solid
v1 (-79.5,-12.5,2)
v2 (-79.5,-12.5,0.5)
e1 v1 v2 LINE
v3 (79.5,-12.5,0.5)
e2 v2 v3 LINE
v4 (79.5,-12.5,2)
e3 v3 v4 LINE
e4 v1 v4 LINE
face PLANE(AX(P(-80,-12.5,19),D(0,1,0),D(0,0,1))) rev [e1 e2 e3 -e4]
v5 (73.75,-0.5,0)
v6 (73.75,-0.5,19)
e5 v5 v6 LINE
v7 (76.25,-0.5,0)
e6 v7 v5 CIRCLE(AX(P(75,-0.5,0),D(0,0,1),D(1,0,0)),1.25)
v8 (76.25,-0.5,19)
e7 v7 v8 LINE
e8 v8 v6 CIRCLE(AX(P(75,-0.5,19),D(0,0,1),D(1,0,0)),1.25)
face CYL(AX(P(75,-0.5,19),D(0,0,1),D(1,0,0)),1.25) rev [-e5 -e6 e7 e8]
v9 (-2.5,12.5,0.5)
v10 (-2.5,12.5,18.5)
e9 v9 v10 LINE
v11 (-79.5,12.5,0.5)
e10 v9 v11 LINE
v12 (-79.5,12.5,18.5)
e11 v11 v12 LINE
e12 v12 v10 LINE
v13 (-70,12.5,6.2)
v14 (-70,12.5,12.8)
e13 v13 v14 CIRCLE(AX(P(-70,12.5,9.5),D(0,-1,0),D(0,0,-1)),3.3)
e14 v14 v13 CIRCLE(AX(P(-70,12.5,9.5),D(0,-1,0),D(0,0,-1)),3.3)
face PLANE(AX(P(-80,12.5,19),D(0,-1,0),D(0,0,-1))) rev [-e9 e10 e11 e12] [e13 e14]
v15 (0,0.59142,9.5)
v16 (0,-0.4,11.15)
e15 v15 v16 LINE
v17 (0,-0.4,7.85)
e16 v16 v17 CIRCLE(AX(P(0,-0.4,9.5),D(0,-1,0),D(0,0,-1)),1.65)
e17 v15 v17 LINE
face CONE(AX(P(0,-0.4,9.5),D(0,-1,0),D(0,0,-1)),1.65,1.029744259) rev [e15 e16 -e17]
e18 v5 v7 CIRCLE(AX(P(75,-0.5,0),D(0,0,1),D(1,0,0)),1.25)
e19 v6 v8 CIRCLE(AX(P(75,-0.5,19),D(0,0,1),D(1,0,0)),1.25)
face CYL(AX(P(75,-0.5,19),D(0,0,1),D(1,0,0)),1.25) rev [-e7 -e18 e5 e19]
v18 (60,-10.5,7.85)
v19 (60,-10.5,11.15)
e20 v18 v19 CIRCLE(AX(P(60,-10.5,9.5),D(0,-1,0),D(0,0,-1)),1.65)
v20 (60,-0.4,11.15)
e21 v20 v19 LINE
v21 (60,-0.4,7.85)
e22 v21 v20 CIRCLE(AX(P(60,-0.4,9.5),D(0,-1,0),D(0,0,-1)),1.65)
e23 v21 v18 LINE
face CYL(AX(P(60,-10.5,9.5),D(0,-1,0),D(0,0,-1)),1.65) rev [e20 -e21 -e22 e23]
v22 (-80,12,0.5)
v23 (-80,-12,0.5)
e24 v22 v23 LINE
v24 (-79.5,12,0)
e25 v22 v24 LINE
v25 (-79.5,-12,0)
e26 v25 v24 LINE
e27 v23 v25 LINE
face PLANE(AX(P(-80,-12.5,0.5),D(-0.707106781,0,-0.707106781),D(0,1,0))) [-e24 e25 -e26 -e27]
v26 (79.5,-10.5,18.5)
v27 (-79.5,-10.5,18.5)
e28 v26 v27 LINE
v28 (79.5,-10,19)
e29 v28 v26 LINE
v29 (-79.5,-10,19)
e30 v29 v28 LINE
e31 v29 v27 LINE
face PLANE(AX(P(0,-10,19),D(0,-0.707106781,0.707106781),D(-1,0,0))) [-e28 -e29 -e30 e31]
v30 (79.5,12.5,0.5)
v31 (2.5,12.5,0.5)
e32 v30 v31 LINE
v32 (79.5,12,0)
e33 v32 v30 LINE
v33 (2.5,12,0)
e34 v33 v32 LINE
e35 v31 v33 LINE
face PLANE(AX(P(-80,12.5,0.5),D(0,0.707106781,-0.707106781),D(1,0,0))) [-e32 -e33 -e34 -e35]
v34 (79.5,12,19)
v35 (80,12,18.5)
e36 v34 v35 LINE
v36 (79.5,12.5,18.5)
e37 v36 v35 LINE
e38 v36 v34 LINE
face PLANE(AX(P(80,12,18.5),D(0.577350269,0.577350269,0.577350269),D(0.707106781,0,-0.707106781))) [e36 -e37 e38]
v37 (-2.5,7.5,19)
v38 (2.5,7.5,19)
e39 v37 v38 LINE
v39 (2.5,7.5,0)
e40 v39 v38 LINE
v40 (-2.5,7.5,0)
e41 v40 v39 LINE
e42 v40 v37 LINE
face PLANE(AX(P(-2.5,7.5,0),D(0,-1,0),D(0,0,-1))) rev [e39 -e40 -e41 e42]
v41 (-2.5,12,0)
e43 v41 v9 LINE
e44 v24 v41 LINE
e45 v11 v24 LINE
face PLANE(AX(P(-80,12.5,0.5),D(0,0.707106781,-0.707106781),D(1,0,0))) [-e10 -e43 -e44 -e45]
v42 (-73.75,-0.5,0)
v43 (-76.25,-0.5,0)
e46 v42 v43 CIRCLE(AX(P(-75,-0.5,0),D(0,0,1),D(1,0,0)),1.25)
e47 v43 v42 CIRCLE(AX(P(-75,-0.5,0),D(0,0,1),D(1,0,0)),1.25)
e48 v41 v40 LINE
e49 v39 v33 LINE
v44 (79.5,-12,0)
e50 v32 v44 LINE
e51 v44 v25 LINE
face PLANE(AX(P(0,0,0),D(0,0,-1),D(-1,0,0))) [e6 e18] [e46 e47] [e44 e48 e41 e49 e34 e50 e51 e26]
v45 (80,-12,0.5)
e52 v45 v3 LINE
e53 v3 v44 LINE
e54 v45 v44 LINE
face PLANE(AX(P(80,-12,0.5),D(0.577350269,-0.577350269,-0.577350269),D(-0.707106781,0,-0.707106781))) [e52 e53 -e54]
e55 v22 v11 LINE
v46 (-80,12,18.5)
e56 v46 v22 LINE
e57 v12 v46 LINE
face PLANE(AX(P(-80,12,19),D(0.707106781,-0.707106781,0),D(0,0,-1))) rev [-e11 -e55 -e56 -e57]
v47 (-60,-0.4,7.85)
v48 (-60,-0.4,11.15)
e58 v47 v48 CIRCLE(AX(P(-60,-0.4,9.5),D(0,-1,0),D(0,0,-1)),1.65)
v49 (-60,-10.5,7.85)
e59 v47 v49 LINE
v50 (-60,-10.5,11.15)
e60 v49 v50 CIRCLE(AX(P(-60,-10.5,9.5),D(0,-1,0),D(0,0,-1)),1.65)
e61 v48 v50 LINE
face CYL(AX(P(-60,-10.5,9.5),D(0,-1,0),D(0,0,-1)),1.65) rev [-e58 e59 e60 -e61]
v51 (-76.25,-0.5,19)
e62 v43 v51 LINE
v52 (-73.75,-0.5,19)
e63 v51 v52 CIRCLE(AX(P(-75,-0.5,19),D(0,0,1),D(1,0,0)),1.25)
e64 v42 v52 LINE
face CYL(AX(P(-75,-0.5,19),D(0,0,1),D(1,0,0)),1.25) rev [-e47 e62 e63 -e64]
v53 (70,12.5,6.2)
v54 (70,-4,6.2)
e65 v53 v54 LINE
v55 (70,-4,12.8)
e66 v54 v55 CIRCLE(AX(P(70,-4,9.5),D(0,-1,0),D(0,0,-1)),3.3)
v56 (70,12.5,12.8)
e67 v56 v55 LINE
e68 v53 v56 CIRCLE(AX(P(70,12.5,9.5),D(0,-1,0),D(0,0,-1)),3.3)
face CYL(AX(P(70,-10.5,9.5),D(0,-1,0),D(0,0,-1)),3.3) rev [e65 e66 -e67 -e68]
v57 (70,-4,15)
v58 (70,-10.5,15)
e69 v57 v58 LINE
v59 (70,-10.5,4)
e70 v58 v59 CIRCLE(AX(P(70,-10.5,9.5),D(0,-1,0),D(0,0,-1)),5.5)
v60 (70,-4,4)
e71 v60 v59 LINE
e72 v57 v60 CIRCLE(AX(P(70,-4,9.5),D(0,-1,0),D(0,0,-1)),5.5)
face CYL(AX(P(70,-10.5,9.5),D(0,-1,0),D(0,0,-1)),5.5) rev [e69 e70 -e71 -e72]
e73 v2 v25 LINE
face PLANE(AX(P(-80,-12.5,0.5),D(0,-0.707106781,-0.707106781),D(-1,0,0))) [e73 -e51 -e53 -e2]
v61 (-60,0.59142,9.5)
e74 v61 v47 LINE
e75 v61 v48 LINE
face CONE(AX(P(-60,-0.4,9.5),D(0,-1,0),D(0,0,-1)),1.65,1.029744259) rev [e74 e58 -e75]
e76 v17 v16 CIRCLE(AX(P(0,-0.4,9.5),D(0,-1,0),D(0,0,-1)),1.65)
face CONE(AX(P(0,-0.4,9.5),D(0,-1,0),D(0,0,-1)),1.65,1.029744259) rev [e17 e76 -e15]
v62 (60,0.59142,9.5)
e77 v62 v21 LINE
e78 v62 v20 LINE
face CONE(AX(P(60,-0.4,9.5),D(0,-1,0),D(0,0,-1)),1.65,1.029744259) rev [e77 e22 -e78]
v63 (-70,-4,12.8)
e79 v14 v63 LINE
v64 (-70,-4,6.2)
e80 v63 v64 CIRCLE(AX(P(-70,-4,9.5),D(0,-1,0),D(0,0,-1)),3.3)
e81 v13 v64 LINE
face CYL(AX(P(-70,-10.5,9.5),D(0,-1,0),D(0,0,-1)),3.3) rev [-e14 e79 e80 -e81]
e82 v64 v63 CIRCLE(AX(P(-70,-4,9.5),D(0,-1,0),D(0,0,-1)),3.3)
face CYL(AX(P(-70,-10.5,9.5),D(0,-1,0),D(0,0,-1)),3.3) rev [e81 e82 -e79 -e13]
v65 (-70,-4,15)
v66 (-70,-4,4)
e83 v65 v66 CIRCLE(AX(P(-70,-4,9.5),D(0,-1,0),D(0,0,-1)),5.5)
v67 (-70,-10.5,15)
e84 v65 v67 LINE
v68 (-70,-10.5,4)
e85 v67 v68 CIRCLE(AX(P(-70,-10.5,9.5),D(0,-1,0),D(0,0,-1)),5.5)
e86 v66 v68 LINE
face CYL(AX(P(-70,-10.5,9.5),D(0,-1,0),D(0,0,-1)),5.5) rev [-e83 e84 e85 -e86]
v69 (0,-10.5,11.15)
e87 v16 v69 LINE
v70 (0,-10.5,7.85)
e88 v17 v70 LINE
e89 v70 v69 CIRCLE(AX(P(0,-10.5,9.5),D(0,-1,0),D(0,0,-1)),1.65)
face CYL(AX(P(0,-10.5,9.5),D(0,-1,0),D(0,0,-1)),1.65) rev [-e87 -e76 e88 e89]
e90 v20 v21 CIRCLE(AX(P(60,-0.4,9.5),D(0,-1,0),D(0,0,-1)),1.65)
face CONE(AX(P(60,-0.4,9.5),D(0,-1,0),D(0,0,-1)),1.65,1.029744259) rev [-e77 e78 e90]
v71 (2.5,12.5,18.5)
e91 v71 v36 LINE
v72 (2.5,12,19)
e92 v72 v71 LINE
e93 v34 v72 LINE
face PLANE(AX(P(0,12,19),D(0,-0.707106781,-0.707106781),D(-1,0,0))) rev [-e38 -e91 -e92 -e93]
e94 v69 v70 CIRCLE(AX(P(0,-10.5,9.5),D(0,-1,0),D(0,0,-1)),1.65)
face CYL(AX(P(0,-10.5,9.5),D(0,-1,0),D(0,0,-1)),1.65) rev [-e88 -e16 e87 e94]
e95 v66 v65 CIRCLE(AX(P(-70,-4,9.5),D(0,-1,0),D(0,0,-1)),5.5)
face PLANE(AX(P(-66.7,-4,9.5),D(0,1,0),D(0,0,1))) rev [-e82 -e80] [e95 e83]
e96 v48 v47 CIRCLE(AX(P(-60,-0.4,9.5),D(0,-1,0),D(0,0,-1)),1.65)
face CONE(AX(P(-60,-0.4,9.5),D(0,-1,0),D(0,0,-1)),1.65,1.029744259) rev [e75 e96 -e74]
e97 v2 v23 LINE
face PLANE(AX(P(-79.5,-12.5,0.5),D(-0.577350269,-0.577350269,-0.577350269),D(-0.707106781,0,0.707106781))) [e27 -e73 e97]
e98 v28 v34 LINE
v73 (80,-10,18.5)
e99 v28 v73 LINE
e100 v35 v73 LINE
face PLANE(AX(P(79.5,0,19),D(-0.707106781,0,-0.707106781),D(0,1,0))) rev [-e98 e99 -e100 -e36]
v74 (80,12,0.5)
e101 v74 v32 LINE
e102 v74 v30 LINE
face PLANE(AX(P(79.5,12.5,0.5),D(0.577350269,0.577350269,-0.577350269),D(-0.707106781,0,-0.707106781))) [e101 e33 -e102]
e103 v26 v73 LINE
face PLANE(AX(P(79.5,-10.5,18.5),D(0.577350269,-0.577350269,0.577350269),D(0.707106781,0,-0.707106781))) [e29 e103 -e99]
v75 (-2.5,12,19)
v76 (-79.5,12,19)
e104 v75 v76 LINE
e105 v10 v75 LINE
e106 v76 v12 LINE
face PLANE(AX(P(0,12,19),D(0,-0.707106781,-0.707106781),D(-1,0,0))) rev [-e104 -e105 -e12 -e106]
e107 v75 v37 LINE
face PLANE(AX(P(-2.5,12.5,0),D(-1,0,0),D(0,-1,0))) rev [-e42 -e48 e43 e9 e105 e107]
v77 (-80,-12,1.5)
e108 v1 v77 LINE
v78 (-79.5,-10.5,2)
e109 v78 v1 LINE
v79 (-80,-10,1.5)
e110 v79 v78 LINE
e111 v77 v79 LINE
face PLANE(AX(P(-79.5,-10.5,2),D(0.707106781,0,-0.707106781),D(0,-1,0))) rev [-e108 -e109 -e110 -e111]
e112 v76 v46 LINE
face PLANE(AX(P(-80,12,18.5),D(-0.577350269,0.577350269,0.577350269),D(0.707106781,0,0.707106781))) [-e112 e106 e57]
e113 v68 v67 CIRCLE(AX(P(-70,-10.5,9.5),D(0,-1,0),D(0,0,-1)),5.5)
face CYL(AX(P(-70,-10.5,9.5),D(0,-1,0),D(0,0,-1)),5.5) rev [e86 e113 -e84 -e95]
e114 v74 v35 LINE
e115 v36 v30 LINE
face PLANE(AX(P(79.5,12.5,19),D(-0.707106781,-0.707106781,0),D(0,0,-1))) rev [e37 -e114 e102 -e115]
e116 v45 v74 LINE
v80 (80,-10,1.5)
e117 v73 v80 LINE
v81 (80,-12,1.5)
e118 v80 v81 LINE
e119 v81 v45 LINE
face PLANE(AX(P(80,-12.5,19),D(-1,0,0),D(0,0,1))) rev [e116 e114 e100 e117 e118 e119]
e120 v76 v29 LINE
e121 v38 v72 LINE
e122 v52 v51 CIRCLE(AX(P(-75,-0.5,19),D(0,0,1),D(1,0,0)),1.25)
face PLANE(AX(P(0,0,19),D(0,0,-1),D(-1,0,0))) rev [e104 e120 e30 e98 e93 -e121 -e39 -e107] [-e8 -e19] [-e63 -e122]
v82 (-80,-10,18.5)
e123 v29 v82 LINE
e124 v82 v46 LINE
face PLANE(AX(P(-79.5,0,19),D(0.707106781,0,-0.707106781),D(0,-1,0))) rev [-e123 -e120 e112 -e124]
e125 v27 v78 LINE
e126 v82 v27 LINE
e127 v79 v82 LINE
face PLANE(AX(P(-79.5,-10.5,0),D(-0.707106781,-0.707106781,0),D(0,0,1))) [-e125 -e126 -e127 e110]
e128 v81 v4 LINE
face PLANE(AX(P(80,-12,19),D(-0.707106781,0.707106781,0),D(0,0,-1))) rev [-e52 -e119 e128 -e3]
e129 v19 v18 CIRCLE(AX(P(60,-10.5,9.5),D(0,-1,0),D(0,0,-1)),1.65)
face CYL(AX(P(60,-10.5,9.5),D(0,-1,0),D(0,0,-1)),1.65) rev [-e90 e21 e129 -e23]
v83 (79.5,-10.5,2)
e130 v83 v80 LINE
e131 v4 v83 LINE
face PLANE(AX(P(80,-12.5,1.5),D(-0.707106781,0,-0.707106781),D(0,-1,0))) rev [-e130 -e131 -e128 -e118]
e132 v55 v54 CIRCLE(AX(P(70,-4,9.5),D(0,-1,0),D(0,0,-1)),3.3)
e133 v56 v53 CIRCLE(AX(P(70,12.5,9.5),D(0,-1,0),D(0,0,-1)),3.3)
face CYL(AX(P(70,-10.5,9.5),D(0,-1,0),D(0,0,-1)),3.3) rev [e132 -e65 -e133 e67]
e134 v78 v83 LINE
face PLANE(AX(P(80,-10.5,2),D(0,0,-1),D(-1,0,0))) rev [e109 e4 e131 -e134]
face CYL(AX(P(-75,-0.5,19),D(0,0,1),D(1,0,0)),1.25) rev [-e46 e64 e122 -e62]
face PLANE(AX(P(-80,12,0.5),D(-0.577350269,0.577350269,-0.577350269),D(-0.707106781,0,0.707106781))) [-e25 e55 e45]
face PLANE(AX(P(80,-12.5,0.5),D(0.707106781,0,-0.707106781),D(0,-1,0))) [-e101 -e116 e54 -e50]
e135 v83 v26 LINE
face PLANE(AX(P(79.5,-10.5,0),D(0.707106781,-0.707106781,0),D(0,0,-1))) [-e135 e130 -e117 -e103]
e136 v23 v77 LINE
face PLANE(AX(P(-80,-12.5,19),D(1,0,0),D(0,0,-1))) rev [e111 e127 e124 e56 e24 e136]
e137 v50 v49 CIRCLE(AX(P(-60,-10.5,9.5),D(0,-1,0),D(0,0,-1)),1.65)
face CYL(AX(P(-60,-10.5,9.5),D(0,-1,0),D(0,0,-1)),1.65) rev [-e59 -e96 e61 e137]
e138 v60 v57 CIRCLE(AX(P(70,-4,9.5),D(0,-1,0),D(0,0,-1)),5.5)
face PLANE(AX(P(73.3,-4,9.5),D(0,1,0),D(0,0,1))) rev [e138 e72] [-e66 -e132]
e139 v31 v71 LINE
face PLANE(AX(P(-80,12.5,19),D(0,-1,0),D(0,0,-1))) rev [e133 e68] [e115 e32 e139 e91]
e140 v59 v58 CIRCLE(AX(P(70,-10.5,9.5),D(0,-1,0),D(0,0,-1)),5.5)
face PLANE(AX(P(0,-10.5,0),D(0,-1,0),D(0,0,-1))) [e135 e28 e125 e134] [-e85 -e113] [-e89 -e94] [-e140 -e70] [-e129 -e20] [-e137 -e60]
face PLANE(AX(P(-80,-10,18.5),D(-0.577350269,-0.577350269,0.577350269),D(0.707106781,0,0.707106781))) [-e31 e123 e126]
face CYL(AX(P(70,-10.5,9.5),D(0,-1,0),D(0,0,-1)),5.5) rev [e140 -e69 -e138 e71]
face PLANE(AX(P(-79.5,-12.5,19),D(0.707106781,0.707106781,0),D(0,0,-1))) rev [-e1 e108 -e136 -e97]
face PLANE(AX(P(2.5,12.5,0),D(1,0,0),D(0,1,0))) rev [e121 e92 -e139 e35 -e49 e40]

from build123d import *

# Parameters (mm, degrees)
SKETCH_1_W                   = 160
SKETCH_1_H                   = 25
EXTRUDE_1_DEPTH              = 19
SKETCH_2_W                   = 160
SKETCH_2_H                   = 15
CUT_EXTRUDE_1_DEPTH          = 2
HOLE_WIZARD_M4_1_D           = 3.3
HOLE_WIZARD_M4_1_DEPTH       = 10.1
HOLE_WIZARD_M4_1_TIP         = 0.991420021
HOLE_WIZARD_M6_1_D           = 6.6
HOLE_WIZARD_M6_1_CBORE_D     = 11
HOLE_WIZARD_M6_1_CBORE_DEPTH = 6.5
SKETCH_7_W                   = 5
SKETCH_7_H                   = 5
CUT_EXTRUDE_2_DEPTH          = 84.170006613
SKETCH_10_W                  = 2
SKETCH_10_H                  = 2
CUT_EXTRUDE_3_DEPTH          = 162.608322805
CHAMFER_1_SIZE               = 0.5
HOLE_WIZARD_M3_1_D           = 2.5


with BuildPart() as part:
    # 草图1 → 凸台-拉伸1 (new body)
    with BuildSketch(Plane.XY):
        Rectangle(SKETCH_1_W, SKETCH_1_H)
    extrude(amount=EXTRUDE_1_DEPTH)

    # 草图2 → 切除-拉伸1 (cut)
    with BuildSketch(Plane.XZ.offset(12.5)):
        with Locations((0, 9.5)):
            Rectangle(SKETCH_2_W, SKETCH_2_H)
    extrude(amount=-CUT_EXTRUDE_1_DEPTH, mode=Mode.SUBTRACT)

    # M4 螺纹孔1
    with Locations(Plane(origin=(0, -10.5, 0), x_dir=(-1, 0, 0), z_dir=(0, -1, 0))):
        with Locations((-60, -9.5), (0, -9.5), (60, -9.5)):
            Hole(HOLE_WIZARD_M4_1_D / 2, depth=HOLE_WIZARD_M4_1_DEPTH)
            with Locations((0, 0, -(HOLE_WIZARD_M4_1_DEPTH + HOLE_WIZARD_M4_1_TIP / 2))):  # 118° drill point
                Cone(0, HOLE_WIZARD_M4_1_D / 2, HOLE_WIZARD_M4_1_TIP, mode=Mode.SUBTRACT)

    # M6 六角凹头螺钉的柱形沉头孔1 (through all)
    with Locations(Plane(origin=(0, -10.5, 0), x_dir=(-1, 0, 0), z_dir=(0, -1, 0))):
        with Locations((-70, -9.5), (70, -9.5)):
            CounterBoreHole(HOLE_WIZARD_M6_1_D / 2, HOLE_WIZARD_M6_1_CBORE_D / 2, HOLE_WIZARD_M6_1_CBORE_DEPTH)

    # 草图7 → 切除-拉伸2 (cut, through all)
    with BuildSketch(Plane.XY.offset(19)):
        with Locations((0, 10)):
            Rectangle(SKETCH_7_W, SKETCH_7_H)
    extrude(amount=-CUT_EXTRUDE_2_DEPTH, mode=Mode.SUBTRACT)

    # 草图10 → 切除-拉伸3 (cut, through all)
    with BuildSketch(Plane(origin=(80, 0, 0), x_dir=(0, 0, -1), z_dir=(1, 0, 0))):
        with Locations((-18, -11.5)):
            Rectangle(SKETCH_10_W, SKETCH_10_H)
    extrude(amount=-CUT_EXTRUDE_3_DEPTH, mode=Mode.SUBTRACT)

    # 倒角1
    chamfer_1_edges = [part.edges().sort_by_distance(p)[0] for p in [
        (-80, 1, 19),
        (80, -12.5, 1),
        (-80, -12.5, 1),
        (80, -10.5, 10.5),
        (80, -11.5, 2),
        (-80, -10.5, 10.5),
        (-80, -11.5, 2),
        (0, -12.5, 0),
        (-80, 0, 0),
        (41.25, 12.5, 0),
        (80, 0, 0),
        (-41.25, 12.5, 0),
        (-41.25, 12.5, 19),
        (41.25, 12.5, 19),
        (-80, 12.5, 9.5),
        (80, 1, 19),
        (80, 12.5, 9.5),
        (0, -10.5, 19),
    ]]
    chamfer(chamfer_1_edges, length=CHAMFER_1_SIZE)

    # M3 螺纹孔1 (through all)
    with Locations(Plane.XY.offset(19)):
        with Locations((75, -0.5), (-75, -0.5)):
            Hole(HOLE_WIZARD_M3_1_D / 2)


solid = part.part
